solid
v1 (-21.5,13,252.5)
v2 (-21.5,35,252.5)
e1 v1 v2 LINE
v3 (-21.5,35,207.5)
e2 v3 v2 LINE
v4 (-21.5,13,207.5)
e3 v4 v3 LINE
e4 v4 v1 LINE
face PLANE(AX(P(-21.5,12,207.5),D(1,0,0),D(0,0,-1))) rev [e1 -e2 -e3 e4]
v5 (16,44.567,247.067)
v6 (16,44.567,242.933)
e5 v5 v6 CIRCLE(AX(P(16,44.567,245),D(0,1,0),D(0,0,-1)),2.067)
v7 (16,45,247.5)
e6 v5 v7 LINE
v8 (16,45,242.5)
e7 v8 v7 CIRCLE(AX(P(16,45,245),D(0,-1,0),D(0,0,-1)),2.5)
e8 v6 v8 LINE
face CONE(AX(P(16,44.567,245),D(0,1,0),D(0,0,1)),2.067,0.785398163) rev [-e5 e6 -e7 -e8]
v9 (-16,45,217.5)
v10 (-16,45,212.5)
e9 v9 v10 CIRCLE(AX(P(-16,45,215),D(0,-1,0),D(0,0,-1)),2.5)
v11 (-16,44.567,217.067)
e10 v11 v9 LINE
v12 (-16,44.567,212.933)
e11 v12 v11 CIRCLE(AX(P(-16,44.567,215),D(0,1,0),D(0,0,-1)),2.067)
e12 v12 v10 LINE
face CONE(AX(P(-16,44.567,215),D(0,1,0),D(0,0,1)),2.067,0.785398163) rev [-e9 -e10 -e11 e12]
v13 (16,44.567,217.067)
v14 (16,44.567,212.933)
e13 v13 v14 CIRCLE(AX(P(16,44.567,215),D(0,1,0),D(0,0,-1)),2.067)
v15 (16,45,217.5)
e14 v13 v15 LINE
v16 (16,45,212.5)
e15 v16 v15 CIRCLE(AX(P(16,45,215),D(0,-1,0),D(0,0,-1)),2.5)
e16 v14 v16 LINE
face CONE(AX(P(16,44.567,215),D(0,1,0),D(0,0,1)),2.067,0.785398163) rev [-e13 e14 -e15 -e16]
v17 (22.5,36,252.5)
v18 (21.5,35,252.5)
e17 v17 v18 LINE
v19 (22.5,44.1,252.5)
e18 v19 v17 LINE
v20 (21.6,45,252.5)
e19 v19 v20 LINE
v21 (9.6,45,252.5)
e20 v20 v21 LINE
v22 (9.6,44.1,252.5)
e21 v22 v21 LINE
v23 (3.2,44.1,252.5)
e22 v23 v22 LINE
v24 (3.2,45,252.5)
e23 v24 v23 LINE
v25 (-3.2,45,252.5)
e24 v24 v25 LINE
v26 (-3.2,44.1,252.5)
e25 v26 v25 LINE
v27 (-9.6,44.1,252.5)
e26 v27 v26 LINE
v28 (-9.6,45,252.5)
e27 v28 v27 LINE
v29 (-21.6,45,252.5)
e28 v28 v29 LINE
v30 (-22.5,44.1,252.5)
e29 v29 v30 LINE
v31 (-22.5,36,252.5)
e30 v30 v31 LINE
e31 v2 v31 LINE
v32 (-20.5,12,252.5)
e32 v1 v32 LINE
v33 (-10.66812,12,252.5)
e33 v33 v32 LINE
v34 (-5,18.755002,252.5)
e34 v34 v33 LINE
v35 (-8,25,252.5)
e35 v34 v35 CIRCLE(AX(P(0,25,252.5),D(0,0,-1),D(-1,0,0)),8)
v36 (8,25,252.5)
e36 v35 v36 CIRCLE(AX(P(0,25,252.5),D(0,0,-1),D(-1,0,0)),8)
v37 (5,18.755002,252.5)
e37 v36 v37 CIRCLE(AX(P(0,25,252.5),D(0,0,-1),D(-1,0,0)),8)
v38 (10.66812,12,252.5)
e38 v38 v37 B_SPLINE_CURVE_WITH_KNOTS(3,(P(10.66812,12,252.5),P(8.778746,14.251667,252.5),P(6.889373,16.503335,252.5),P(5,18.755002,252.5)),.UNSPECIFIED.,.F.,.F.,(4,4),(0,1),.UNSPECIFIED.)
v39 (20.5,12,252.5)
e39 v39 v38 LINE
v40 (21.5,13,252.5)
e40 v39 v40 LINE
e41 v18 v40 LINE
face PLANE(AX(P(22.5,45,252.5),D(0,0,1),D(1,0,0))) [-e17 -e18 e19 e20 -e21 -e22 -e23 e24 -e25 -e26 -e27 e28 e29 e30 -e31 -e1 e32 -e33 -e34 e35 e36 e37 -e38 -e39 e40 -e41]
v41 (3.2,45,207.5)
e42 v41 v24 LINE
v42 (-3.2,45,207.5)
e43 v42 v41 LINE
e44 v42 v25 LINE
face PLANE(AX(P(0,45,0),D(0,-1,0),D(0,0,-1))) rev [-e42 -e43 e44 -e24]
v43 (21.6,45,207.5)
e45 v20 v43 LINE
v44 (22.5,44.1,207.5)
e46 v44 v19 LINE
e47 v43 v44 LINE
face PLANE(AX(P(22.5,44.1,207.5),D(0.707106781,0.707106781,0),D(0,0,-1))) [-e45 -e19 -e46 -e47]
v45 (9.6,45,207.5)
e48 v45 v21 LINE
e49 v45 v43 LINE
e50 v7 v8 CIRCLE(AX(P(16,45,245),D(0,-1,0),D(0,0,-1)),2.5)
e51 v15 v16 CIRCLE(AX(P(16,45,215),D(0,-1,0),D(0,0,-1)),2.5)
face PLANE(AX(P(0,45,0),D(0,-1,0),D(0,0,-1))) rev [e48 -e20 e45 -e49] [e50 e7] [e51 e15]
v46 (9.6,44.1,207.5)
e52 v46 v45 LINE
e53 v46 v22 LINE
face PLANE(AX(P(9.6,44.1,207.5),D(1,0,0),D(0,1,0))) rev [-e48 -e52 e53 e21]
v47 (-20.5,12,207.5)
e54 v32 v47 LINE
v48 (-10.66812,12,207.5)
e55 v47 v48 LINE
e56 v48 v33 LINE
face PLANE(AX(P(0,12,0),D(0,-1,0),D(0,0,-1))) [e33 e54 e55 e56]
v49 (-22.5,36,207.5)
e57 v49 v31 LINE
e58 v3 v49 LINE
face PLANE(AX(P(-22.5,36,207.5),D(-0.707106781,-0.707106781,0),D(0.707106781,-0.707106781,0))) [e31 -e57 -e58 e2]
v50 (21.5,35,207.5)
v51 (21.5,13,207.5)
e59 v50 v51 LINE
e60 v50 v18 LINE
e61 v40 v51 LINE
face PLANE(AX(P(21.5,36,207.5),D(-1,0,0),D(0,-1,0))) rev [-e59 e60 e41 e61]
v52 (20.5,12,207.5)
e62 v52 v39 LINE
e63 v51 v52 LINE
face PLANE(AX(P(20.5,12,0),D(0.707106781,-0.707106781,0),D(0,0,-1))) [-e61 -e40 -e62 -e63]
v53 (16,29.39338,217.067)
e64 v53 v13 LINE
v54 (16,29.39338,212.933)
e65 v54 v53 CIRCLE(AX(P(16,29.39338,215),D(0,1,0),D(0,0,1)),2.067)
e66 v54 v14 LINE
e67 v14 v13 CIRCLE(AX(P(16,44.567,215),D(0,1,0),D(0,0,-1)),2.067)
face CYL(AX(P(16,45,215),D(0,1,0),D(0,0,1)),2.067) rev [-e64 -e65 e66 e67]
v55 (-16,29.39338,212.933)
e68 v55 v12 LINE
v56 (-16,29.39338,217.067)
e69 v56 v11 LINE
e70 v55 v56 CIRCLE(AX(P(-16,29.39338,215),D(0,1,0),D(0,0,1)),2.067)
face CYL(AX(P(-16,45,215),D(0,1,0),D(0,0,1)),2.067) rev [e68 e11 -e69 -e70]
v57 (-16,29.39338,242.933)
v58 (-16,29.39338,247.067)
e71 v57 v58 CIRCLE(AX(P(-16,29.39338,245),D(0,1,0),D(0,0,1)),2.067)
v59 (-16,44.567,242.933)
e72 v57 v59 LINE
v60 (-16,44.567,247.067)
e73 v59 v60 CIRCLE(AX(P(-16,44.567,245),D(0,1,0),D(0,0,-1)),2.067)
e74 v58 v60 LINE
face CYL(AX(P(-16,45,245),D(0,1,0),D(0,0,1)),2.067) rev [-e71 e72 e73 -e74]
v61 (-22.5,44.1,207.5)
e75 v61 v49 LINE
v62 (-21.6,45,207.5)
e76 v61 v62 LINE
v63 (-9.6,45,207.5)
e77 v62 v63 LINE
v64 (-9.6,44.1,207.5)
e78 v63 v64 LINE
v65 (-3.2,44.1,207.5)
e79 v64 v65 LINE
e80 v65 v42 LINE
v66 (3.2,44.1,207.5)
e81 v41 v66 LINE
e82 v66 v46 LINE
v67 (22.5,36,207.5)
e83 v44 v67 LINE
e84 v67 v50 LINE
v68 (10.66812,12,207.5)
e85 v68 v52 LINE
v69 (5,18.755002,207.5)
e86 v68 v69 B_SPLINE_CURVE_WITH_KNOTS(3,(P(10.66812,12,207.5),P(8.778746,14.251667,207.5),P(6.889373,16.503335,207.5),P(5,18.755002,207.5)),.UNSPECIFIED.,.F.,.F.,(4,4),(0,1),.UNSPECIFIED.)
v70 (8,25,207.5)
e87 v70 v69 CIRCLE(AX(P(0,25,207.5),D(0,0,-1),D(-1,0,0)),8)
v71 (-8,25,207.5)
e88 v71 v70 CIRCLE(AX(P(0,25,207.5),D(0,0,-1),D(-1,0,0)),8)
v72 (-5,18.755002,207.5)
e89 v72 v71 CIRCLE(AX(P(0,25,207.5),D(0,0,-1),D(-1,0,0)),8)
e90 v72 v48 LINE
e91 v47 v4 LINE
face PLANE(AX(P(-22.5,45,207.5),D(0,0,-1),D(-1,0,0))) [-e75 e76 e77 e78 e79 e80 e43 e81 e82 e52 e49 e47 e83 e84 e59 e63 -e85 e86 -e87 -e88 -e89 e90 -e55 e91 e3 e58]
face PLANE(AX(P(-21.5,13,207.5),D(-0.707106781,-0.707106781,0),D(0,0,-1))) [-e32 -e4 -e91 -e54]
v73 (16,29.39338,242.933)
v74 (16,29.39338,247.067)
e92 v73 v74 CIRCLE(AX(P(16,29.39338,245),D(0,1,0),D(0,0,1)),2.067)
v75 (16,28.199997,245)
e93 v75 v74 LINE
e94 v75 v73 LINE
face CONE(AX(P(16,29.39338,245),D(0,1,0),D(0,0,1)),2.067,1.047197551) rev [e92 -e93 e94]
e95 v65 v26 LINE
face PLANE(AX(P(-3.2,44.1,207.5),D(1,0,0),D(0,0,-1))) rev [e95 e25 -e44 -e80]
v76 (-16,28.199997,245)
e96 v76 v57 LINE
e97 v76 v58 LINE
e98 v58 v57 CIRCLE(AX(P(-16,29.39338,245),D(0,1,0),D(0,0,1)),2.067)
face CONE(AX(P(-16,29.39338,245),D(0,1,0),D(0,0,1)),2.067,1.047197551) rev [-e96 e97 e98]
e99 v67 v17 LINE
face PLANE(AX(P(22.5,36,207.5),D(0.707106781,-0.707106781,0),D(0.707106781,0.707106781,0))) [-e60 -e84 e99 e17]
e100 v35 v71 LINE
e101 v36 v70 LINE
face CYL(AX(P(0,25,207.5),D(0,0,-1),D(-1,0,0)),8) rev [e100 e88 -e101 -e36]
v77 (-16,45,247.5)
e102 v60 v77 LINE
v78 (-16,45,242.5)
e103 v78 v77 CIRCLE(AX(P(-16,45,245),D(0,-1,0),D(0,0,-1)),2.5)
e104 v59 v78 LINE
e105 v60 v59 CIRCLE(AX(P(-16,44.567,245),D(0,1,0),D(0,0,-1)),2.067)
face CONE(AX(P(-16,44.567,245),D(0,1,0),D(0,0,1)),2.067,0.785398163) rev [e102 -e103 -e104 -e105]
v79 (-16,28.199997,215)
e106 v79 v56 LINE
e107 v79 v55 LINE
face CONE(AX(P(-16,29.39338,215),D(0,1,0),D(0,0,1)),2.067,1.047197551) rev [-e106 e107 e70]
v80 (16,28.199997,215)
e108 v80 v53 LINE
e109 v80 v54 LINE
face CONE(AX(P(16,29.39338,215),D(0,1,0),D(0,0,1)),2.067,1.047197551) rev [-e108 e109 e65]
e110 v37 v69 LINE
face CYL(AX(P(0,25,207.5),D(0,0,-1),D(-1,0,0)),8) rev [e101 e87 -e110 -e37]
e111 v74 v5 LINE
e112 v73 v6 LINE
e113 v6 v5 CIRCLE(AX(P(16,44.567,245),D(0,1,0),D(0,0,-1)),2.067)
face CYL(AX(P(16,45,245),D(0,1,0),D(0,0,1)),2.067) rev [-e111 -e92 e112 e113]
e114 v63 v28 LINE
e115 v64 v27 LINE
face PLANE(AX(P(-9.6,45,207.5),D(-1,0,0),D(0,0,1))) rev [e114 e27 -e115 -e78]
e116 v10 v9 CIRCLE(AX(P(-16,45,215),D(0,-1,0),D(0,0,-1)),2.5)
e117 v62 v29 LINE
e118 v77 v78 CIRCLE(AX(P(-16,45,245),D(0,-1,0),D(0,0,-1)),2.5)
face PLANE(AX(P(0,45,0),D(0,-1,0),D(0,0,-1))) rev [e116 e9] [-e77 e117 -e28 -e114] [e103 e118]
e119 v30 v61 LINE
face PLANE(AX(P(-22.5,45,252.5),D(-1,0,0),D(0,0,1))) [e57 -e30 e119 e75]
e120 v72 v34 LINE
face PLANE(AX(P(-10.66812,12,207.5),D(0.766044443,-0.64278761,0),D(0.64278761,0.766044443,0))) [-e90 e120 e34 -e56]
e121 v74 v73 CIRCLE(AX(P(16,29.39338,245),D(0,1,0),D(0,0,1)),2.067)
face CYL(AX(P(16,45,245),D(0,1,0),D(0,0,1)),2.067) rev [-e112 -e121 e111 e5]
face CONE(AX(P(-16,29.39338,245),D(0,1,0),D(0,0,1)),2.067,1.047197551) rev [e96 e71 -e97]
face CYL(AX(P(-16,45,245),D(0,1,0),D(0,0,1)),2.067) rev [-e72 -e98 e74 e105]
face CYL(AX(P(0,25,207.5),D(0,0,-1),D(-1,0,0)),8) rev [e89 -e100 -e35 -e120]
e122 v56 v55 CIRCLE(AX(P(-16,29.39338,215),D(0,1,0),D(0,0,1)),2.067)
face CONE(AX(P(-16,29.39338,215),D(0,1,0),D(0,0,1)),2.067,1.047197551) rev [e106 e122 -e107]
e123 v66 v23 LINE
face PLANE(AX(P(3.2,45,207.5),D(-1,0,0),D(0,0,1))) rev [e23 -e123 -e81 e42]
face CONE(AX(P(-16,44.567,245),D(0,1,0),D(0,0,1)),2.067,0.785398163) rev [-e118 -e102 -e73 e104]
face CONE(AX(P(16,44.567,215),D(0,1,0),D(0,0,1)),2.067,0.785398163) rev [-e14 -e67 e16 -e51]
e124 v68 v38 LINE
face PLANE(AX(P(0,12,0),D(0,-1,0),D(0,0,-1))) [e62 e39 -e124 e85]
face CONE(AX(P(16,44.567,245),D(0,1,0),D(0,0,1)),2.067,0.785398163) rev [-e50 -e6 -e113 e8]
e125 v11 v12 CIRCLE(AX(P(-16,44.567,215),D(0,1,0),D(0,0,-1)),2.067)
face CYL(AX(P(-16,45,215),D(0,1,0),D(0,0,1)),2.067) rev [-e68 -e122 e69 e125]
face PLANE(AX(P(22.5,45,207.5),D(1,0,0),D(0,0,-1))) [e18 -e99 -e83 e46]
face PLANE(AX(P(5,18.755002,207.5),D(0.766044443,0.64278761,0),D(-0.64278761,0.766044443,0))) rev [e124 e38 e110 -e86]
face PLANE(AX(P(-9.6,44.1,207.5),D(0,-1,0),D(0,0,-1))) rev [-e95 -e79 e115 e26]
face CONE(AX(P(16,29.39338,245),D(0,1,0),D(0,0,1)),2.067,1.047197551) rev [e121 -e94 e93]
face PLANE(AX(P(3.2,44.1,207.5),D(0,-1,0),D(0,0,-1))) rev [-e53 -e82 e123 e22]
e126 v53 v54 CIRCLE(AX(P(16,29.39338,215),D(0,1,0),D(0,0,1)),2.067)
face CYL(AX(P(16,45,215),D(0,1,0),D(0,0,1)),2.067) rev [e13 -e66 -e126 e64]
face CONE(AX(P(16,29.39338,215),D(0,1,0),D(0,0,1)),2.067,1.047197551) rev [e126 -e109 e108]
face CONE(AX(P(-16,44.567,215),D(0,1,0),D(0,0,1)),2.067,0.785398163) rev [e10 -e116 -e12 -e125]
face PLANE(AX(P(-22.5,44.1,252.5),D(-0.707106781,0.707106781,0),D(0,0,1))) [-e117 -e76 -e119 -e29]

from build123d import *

# Parameters (mm, degrees)
SKETCH_1_W               = 45
SKETCH_1_H               = 45
EXTRUDE_1_DEPTH          = 33
SKETCH_2_W               = 6.4
SKETCH_2_H               = 0.9
CUT_EXTRUDE_1_DEPTH      = 68.5
SKETCH_3_W               = 6.4
SKETCH_3_H               = 0.9
CUT_EXTRUDE_2_DEPTH      = 68.5
SKETCH_4_W               = 1
SKETCH_4_H               = 24
CUT_EXTRUDE_3_DEPTH      = 68.5
CUT_EXTRUDE_4_DEPTH      = 68.5
SKETCH_6_W               = 1
SKETCH_6_H               = 24
CUT_EXTRUDE_5_DEPTH      = 68.500000167
DRAFT_1_ANGLE            = 45
DRAFT_2_ANGLE            = 45
DRAFT_3_ANGLE            = 40
HOLE_WIZARD_16_0_16_1_D  = 16.000000007
HOLE_WIZARD_M3_5_1_D     = 4.134
HOLE_WIZARD_M3_5_1_DEPTH = 15.60662
HOLE_WIZARD_M3_5_1_TIP   = 1.193383006
CHAMFER_1_SIZE           = 0.433
CHAMFER_2_SIZE           = 1
CHAMFER_3_SIZE           = 0.9
CUT_EXTRUDE_6_DEPTH      = 106.297198595


with BuildPart() as part:
    # 草图1 → 凸台-拉伸1 (new body)
    with BuildSketch(Plane.XZ.offset(-12)):
        with Locations((0, 230)):
            Rectangle(SKETCH_1_W, SKETCH_1_H)
    extrude(amount=-EXTRUDE_1_DEPTH)

    # 草图2 → 切除-拉伸1 (cut, through all)
    with BuildSketch(Plane.XY.offset(252.5)):
        with Locations((-6.4, 44.55)):
            Rectangle(SKETCH_2_W, SKETCH_2_H)
    extrude(amount=-CUT_EXTRUDE_1_DEPTH, mode=Mode.SUBTRACT)

    # 草图3 → 切除-拉伸2 (cut, through all)
    with BuildSketch(Plane.XY.offset(252.5)):
        with Locations((6.4, 44.55)):
            Rectangle(SKETCH_3_W, SKETCH_3_H)
    extrude(amount=-CUT_EXTRUDE_2_DEPTH, mode=Mode.SUBTRACT)

    # 草图4 → 切除-拉伸3 (cut, through all)
    with BuildSketch(Plane.XY.offset(252.5)):
        with Locations((22, 24)):
            Rectangle(SKETCH_4_W, SKETCH_4_H)
    extrude(amount=-CUT_EXTRUDE_3_DEPTH, mode=Mode.SUBTRACT)

    # 草图5 → 切除-拉伸4 (cut, through all)
    with BuildSketch(Plane.XY.offset(252.5)):
        with BuildLine():
            Line((-10.668119688, 12), (10.668119688, 12))
            add(Edge.make_bspline(
                [(5, 18.755002002), (6.889373229, 16.503334668), (8.778746459, 14.251667334), (10.668119688, 12)],
                knots=[0, 0, 0, 0, 1, 1, 1, 1], degree=3))
            Line((5, 18.755002002), (-10.668119688, 37.427539929))
            Line((-10.668119688, 37.427539929), (-10.668119688, 12))
        make_face()
    extrude(amount=-CUT_EXTRUDE_4_DEPTH, mode=Mode.SUBTRACT)

    # 草图6 → 切除-拉伸5 (cut, through all)
    with BuildSketch(Plane.XY.offset(252.5)):
        with Locations((-22, 24)):
            Rectangle(SKETCH_6_W, SKETCH_6_H)
    extrude(amount=-CUT_EXTRUDE_5_DEPTH, mode=Mode.SUBTRACT)

    # 拔模1
    draft_1_faces = [part.faces().sort_by_distance(p)[0] for p in [
        (-22, 36, 230),
    ]]
    draft(draft_1_faces, Plane(origin=(-22.5, 45, 252.5), x_dir=(0, 0, -1), z_dir=(-1, 0, 0)), DRAFT_1_ANGLE)

    # 拔模2
    draft_2_faces = [part.faces().sort_by_distance(p)[0] for p in [
        (22, 36, 230),
    ]]
    draft(draft_2_faces, Plane(origin=(22.5, 45, 207.5), x_dir=(0, 0, 1), z_dir=(1, 0, 0)), DRAFT_2_ANGLE)

    # 拔模3
    draft_3_faces = [part.faces().sort_by_distance(p)[0] for p in [
        (-10.668119688, 24.713769965, 230),
    ]]
    draft(draft_3_faces, Plane(origin=(0, 12, 0), x_dir=(0, 0, -1), z_dir=(0, -1, 0)), DRAFT_3_ANGLE)

    # Ø16.0 (16) 直径孔1 (through all)
    with Locations(Plane(origin=(0, 0, 207.5), x_dir=(-1, 0, 0), z_dir=(0, 0, -1))):
        with Locations((0, 25)):
            Hole(HOLE_WIZARD_16_0_16_1_D / 2)

    # M3.5 间隙孔1
    with Locations(Plane(origin=(0, 45, 0), x_dir=(1, 0, 0), z_dir=(0, 1, 0))):
        with Locations((16, -215), (16, -245), (-16, -215), (-16, -245)):
            Hole(HOLE_WIZARD_M3_5_1_D / 2, depth=HOLE_WIZARD_M3_5_1_DEPTH)
            with Locations((0, 0, -(HOLE_WIZARD_M3_5_1_DEPTH + HOLE_WIZARD_M3_5_1_TIP / 2))):  # 120° drill point
                Cone(0, HOLE_WIZARD_M3_5_1_D / 2, HOLE_WIZARD_M3_5_1_TIP, mode=Mode.SUBTRACT)

    # 倒角1
    chamfer_1_edges = [part.edges().sort_by_distance(p)[0] for p in [
        (-13.933, 45, 245),
        (-13.933, 45, 215),
        (18.067, 45, 245),
        (18.067, 45, 215),
    ]]
    chamfer(chamfer_1_edges, length=CHAMFER_1_SIZE)

    # 倒角2
    chamfer_2_edges = [part.edges().sort_by_distance(p)[0] for p in [
        (21.5, 12, 230),
        (-21.5, 12, 230),
    ]]
    chamfer(chamfer_2_edges, length=CHAMFER_2_SIZE)

    # 倒角3
    chamfer_3_edges = [part.edges().sort_by_distance(p)[0] for p in [
        (-22.5, 45, 230),
        (22.5, 45, 230),
    ]]
    chamfer(chamfer_3_edges, length=CHAMFER_3_SIZE)

    # 草图11 → 切除-拉伸6 (cut, through all)
    with BuildSketch(Plane.XY.offset(300)):
        with BuildLine():
            Line((-9.25, 11.7), (-9.25, 5))
            Line((-9.25, 5), (-20, 5))
            Line((-20, 5), (-20, 0))
            Line((-20, 0), (20, 0))
            Line((20, 0), (20, 5))
            Line((20, 5), (9.25, 5))
            Line((9.25, 5), (9.25, 11.7))
            Line((9.25, 11.7), (9.11850775, 11.7))
            Line((9.11850775, 11.7), (4, 17.8))
            Line((4, 17.8), (3.487119155, 17.8))
            ThreePointArc((3.487119155, 17.8), (0, 33), (-3.487119155, 17.8))
            Line((-3.487119155, 17.8), (-4, 17.8))
            Line((-4, 17.8), (-9.11850775, 11.7))
            Line((-9.11850775, 11.7), (-9.25, 11.7))
        make_face()
    extrude(amount=-CUT_EXTRUDE_6_DEPTH, mode=Mode.SUBTRACT)


solid = part.part
